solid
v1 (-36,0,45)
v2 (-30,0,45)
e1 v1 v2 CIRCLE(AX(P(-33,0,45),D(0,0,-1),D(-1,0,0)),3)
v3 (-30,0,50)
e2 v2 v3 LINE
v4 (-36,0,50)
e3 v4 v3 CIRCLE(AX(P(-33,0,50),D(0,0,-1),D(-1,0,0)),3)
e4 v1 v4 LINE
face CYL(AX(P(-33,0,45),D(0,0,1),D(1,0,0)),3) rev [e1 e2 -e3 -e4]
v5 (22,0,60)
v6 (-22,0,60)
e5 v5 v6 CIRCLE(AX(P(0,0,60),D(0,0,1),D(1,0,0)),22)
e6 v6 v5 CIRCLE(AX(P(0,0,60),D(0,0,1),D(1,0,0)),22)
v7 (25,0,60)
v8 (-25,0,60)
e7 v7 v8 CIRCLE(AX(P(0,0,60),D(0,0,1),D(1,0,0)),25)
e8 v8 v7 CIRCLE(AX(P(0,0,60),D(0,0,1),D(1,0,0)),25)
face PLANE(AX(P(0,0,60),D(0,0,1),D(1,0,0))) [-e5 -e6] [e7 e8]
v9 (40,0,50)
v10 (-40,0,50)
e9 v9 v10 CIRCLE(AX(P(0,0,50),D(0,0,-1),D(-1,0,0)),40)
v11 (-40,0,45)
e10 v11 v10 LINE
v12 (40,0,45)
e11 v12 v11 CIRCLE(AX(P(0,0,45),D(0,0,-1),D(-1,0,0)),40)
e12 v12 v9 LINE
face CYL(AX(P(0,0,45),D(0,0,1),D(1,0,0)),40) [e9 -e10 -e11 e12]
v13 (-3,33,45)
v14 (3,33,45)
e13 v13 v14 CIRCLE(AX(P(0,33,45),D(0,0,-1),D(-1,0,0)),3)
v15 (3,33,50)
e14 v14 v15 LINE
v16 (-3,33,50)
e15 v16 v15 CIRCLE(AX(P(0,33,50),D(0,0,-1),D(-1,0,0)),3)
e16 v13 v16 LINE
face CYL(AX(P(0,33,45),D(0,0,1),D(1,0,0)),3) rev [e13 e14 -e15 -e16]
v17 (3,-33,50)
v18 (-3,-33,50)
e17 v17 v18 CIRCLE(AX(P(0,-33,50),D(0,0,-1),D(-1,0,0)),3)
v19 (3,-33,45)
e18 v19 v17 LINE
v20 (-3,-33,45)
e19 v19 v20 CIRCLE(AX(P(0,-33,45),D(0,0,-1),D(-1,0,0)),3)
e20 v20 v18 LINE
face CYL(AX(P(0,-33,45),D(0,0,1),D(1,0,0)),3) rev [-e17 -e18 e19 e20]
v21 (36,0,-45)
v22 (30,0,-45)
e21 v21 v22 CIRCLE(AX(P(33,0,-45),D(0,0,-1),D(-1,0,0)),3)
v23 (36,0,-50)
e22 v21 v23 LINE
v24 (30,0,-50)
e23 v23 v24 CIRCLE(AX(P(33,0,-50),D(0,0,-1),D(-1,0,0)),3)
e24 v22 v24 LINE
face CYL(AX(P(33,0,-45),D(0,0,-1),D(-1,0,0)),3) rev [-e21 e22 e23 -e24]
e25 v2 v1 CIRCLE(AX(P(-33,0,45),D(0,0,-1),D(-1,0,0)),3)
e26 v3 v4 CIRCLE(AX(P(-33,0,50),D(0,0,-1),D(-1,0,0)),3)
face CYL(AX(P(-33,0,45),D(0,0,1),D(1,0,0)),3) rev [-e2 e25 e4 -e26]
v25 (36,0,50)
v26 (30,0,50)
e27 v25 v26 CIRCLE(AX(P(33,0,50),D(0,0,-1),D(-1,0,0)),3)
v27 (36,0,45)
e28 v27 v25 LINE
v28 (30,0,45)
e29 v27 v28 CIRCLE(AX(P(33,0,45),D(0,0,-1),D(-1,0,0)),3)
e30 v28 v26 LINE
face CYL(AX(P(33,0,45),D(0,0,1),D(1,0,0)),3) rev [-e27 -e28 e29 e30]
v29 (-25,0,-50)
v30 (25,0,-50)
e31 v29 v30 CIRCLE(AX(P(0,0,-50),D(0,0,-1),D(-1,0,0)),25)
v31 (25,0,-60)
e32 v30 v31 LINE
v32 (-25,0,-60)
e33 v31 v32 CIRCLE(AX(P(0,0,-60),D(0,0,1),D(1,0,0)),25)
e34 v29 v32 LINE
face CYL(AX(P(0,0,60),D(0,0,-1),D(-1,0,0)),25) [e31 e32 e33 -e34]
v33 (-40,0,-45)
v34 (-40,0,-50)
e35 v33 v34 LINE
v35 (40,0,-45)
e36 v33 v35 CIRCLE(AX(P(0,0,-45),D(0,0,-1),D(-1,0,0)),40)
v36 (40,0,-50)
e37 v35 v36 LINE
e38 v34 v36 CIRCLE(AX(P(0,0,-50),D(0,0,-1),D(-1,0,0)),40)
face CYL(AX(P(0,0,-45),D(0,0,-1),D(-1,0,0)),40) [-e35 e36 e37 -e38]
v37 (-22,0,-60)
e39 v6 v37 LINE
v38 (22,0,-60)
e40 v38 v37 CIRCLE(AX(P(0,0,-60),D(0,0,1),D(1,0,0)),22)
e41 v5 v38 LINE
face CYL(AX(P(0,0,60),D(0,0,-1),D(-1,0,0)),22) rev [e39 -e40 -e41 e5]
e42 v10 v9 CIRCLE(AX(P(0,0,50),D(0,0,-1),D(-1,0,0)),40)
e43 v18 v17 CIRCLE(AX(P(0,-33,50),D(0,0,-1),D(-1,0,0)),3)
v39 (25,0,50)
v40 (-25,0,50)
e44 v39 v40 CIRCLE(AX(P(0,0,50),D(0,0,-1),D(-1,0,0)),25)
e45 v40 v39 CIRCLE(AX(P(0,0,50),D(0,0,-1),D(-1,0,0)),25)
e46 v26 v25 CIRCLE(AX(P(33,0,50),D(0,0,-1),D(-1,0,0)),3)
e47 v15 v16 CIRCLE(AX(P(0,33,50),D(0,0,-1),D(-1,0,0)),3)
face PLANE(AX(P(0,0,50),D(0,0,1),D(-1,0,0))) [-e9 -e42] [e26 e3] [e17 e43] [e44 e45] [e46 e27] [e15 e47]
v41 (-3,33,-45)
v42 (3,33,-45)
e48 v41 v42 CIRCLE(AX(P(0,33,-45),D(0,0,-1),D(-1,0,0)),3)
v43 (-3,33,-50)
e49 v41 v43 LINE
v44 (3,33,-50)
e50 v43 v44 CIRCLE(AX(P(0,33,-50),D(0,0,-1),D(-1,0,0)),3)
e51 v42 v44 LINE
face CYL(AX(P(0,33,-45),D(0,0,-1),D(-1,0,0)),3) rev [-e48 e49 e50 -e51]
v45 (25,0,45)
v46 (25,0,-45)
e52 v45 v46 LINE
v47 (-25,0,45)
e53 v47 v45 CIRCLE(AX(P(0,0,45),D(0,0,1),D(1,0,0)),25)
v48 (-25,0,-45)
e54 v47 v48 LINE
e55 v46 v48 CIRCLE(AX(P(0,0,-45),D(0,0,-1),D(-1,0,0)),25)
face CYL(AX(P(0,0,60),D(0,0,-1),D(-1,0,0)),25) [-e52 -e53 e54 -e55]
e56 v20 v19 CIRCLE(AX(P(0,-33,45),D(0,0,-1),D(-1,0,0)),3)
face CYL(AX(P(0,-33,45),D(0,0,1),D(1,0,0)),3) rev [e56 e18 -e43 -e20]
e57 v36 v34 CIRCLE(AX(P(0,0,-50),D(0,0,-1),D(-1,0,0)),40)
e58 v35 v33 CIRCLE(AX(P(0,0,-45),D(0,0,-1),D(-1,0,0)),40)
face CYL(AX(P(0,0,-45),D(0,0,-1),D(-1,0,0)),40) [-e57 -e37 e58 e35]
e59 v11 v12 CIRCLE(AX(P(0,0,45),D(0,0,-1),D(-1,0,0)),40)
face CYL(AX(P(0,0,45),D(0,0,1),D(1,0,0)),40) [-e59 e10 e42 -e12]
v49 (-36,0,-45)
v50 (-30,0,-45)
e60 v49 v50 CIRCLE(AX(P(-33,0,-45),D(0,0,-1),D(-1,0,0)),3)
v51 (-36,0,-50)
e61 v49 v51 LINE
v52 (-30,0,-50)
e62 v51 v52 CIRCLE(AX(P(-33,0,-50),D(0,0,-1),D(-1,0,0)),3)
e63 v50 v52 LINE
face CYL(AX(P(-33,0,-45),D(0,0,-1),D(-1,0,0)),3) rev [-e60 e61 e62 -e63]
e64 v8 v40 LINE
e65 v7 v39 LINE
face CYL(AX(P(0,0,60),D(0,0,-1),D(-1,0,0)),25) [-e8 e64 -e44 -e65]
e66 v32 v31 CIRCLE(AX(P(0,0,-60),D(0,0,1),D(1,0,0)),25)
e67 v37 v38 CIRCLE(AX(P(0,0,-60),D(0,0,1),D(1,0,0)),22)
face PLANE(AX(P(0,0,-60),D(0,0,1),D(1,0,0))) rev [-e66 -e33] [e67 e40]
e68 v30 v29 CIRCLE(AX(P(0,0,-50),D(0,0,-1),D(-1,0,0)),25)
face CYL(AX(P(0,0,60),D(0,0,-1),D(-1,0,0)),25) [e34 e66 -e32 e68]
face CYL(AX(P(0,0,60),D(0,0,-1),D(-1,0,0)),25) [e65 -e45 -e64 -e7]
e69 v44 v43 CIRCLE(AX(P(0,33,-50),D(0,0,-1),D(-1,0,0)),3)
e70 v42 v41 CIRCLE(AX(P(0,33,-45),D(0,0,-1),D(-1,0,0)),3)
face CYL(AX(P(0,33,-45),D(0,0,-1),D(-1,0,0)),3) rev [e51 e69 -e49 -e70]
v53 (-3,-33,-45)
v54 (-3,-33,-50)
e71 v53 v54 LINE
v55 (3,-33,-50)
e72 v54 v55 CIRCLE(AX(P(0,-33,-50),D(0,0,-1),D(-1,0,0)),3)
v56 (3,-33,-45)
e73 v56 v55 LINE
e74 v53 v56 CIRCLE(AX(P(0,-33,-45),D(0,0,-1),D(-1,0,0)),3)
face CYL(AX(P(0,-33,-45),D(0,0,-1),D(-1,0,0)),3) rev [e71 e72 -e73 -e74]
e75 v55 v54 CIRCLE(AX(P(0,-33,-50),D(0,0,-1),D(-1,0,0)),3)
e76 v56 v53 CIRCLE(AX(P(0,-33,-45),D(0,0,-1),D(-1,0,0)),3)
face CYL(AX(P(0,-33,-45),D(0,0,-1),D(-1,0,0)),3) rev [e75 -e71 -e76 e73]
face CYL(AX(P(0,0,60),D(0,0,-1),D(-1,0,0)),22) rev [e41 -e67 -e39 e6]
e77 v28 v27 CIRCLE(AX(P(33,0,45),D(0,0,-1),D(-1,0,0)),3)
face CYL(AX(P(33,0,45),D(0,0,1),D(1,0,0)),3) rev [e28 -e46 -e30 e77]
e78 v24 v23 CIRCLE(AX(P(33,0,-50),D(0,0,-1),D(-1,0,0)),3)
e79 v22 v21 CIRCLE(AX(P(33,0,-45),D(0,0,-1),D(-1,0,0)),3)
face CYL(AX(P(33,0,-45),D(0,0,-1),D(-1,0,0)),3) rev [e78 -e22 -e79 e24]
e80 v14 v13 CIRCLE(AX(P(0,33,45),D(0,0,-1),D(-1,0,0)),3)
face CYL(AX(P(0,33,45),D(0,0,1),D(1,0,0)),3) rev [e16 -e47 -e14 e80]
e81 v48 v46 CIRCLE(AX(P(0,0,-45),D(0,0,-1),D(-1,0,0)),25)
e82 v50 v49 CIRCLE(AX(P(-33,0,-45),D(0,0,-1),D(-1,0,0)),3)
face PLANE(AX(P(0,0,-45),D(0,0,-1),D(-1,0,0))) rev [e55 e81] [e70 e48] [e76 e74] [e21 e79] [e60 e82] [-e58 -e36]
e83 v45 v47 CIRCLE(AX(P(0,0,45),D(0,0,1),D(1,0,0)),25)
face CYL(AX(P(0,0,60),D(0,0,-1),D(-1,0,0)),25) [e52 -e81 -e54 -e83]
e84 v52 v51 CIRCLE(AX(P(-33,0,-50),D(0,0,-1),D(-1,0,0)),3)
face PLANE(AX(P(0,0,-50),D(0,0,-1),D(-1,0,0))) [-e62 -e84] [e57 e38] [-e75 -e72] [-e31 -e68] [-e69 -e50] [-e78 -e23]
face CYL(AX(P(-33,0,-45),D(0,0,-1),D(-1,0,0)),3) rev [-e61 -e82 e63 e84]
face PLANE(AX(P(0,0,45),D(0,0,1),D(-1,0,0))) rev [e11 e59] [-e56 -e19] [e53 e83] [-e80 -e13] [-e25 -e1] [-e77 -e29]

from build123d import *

# Parameters (mm, degrees)
SKETCH1_R           = 25
SKETCH1_R_2         = 22
BOSS_EXTRUDE1_DEPTH = 60
BOSS_EXTRUDE2_START = -15
SKETCH2_R           = 40
SKETCH2_R_2         = 25
SKETCH2_R_3         = 3
BOSS_EXTRUDE2_DEPTH = 5


with BuildPart() as part:
    # Sketch1 → Boss-Extrude1 (new, symmetric)
    with BuildSketch(Plane.XY):
        Circle(SKETCH1_R)
        Circle(SKETCH1_R_2, mode=Mode.SUBTRACT)
    extrude(amount=BOSS_EXTRUDE1_DEPTH, both=True)

    # Sketch2 → Boss-Extrude2 (add)
    with BuildSketch(Plane(origin=(0, 0, -60), x_dir=(-1, 0, 0), z_dir=(0, 0, -1)).offset(BOSS_EXTRUDE2_START)):
        Circle(SKETCH2_R)
        Circle(SKETCH2_R_2, mode=Mode.SUBTRACT)
        with Locations((0, 33)):
            Circle(SKETCH2_R_3, mode=Mode.SUBTRACT)
        with Locations((33, 0)):
            Circle(SKETCH2_R_3, mode=Mode.SUBTRACT)
        with Locations((0, -33)):
            Circle(SKETCH2_R_3, mode=Mode.SUBTRACT)
        with Locations((-33, 0)):
            Circle(SKETCH2_R_3, mode=Mode.SUBTRACT)
    boss_extrude2 = extrude(amount=BOSS_EXTRUDE2_DEPTH)

    # Mirror1: Boss-Extrude2 across plane
    add(boss_extrude2.mirror(Plane.XY))


solid = part.part
